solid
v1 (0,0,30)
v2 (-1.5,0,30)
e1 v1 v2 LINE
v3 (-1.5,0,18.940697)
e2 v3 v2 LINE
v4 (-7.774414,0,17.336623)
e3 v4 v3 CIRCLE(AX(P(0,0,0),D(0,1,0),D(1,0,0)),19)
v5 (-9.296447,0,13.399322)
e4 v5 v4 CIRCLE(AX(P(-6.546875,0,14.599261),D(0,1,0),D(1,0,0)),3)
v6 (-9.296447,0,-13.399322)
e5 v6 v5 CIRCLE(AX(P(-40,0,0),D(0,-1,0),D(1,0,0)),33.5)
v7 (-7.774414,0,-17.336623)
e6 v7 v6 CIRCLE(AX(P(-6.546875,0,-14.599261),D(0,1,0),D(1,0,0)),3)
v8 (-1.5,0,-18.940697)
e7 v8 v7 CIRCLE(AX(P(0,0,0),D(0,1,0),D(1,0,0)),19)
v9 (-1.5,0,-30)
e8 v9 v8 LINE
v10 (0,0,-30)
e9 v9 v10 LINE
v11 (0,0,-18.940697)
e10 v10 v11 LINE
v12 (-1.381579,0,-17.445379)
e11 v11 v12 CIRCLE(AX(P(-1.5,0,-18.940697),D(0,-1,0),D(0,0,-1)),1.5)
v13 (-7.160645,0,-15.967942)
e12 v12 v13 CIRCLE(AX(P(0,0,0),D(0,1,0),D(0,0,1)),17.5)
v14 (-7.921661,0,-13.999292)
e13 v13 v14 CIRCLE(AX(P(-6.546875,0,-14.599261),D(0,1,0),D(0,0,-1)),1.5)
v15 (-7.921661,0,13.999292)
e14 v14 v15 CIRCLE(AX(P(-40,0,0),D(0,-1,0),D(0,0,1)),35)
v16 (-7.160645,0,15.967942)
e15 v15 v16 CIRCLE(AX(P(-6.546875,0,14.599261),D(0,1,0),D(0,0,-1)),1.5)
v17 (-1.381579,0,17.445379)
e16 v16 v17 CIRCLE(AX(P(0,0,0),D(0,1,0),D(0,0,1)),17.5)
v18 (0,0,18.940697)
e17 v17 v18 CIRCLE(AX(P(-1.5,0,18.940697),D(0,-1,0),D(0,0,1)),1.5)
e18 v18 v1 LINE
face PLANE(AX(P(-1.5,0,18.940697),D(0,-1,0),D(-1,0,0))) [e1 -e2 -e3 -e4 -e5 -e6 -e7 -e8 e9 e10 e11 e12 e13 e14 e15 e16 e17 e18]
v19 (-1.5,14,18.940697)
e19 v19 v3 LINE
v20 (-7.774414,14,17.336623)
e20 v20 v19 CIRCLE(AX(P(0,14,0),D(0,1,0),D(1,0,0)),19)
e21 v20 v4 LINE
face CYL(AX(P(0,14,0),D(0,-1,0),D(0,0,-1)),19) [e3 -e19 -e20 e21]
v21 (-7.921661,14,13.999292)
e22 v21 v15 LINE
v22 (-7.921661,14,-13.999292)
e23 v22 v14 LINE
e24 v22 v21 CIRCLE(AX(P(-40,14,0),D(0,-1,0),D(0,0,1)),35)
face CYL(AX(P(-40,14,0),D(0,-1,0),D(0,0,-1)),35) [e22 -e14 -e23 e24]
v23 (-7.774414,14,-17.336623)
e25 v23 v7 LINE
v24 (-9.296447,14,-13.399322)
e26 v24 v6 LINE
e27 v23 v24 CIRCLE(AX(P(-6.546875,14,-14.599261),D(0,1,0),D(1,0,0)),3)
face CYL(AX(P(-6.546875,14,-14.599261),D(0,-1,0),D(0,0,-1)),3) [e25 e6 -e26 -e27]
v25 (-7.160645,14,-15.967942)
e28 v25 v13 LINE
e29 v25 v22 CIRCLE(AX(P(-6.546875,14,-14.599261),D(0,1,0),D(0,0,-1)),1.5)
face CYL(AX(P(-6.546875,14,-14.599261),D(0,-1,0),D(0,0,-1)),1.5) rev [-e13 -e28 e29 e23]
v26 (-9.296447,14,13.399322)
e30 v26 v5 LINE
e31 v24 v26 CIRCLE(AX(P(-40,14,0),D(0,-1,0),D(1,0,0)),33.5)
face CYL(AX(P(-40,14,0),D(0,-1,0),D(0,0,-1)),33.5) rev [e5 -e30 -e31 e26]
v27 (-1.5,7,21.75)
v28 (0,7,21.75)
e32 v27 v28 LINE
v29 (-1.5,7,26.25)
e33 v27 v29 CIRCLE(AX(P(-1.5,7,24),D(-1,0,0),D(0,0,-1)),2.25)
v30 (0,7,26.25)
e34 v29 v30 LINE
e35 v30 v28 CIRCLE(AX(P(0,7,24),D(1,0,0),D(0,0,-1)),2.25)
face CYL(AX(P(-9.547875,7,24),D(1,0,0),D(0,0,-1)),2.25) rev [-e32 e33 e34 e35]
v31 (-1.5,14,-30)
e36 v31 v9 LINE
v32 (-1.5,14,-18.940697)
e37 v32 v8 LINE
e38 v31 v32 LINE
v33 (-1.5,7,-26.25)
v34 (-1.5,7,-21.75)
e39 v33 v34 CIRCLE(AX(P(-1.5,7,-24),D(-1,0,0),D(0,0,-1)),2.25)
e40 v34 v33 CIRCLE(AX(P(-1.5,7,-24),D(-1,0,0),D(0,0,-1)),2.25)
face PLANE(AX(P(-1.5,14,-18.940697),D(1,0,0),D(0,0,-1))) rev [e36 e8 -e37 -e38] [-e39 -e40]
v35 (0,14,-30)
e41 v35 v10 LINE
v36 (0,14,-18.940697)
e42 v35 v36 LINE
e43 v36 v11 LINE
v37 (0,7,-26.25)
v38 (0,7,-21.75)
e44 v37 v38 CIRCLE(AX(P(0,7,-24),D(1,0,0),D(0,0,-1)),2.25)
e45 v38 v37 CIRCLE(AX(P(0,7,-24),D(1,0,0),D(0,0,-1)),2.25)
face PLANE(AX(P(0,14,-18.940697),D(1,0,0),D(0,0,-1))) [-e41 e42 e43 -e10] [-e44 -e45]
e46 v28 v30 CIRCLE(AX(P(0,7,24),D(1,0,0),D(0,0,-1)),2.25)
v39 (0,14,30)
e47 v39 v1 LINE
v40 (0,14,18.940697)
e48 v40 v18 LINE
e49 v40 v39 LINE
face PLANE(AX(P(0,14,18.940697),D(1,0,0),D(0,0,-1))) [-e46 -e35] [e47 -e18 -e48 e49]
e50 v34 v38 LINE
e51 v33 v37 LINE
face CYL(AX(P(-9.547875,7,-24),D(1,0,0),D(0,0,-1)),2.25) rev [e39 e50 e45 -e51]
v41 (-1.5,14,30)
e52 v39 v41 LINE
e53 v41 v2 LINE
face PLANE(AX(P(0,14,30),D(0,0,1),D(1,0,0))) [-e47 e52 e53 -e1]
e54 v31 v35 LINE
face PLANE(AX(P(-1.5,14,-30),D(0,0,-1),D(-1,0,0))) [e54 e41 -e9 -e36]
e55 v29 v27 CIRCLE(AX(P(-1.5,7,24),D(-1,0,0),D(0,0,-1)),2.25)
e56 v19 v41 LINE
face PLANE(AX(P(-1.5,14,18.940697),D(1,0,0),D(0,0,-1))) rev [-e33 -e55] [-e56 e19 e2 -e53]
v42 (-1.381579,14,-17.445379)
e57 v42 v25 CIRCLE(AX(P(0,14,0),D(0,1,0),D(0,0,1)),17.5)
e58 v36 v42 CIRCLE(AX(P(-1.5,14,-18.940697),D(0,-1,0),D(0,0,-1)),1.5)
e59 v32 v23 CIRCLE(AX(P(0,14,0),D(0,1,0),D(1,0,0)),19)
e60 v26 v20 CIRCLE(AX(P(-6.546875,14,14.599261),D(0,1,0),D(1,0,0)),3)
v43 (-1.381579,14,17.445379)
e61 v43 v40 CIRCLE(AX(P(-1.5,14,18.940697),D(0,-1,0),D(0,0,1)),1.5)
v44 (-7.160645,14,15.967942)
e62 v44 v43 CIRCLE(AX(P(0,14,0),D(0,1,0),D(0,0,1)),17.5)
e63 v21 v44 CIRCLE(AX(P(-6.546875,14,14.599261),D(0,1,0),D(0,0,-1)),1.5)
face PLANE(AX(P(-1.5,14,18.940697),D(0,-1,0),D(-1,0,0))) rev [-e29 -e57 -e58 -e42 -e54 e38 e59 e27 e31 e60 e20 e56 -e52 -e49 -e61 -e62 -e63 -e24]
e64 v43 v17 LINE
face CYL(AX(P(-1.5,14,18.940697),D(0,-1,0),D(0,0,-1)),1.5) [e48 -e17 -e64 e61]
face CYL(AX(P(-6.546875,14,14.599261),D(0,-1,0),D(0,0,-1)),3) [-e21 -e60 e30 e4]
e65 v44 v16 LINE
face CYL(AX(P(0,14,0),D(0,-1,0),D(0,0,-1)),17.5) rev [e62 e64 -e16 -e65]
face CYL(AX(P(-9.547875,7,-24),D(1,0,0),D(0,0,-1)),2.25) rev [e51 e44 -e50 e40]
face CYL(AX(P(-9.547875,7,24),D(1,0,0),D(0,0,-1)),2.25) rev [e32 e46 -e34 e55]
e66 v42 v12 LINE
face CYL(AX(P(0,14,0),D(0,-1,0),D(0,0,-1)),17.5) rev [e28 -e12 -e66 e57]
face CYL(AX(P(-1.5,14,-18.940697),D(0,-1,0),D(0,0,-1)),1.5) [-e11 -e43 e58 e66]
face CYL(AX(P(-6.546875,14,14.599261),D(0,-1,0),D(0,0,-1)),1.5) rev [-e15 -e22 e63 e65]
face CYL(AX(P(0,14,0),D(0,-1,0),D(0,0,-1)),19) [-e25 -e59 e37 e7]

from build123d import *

# Parameters (mm, degrees)
EXTRUDE_THIN3_DEPTH = 14
CUT_EXTRUDE2_REACH  = 36.455
SKETCH3_R           = 2.25


with BuildPart() as part:
    # Sketch1 → Extrude-Thin3 (new body)
    with BuildSketch(Plane(origin=(0, 0, 0), x_dir=(1, 0, 0), z_dir=(0, 1, 0))):
        with BuildLine():
            Line((0, -30), (0, -18.940696925))
            ThreePointArc((0, -18.940696925), (-0.398266916, -17.922765586), (-1.381578947, -17.445378747))
            ThreePointArc((-1.381578947, -17.445378747), (-4.334524238, -16.954701402), (-7.160644531, -15.967941943))
            ThreePointArc((-7.160644531, -15.967941943), (-7.945976251, -15.140108401), (-7.921660959, -13.999291567))
            ThreePointArc((-7.921660959, -13.999291567), (-5, 0), (-7.921660959, 13.999291567))
            ThreePointArc((-7.921660959, 13.999291567), (-7.945976251, 15.140108401), (-7.160644531, 15.967941943))
            ThreePointArc((-7.160644531, 15.967941943), (-4.334524238, 16.954701402), (-1.381578947, 17.445378747))
            ThreePointArc((-1.381578947, 17.445378747), (-0.398266916, 17.922765586), (0, 18.940696925))
            Line((0, 18.940696925), (0, 30))
            Line((0, 30), (-1.5, 30))
            Line((-1.5, 30), (-1.5, 18.940696925))
            ThreePointArc((-1.5, 18.940696925), (-4.706054887, 18.407961522), (-7.774414062, 17.336622681))
            ThreePointArc((-7.774414063, 17.336622681), (-9.345077502, 15.680955597), (-9.296446918, 13.399321928))
            ThreePointArc((-9.296446918, 13.399321928), (-6.5, 0), (-9.296446918, -13.399321928))
            ThreePointArc((-9.296446918, -13.399321928), (-9.345077502, -15.680955597), (-7.774414062, -17.336622681))
            ThreePointArc((-7.774414063, -17.336622681), (-4.706054887, -18.407961522), (-1.5, -18.940696925))
            Line((-1.5, -18.940696925), (-1.5, -30))
            Line((-1.5, -30), (0, -30))
        make_face()
    extrude(amount=EXTRUDE_THIN3_DEPTH)

    # Sketch3 → Cut-Extrude2 (cut, up to next)
    with BuildSketch(Plane(origin=(0, 0, 0), x_dir=(0, 0, -1), z_dir=(1, 0, 0)), mode=Mode.PRIVATE) as cut_extrude2_sk1:
        with Locations((-24, 7)):
            Circle(SKETCH3_R)
    cut_extrude2_tool1 = extrude(cut_extrude2_sk1.sketch, amount=-CUT_EXTRUDE2_REACH, mode=Mode.PRIVATE) & part.part
    # Sketch3 → Cut-Extrude2 (cut, up to next)
    with BuildSketch(Plane(origin=(0, 0, 0), x_dir=(0, 0, -1), z_dir=(1, 0, 0)), mode=Mode.PRIVATE) as cut_extrude2_sk2:
        with Locations((24, 7)):
            Circle(SKETCH3_R)
    cut_extrude2_tool2 = extrude(cut_extrude2_sk2.sketch, amount=-CUT_EXTRUDE2_REACH, mode=Mode.PRIVATE) & part.part
    add(cut_extrude2_tool1.solids().sort_by_distance((0, 7, 24))[0], mode=Mode.SUBTRACT)
    add(cut_extrude2_tool2.solids().sort_by_distance((0, 7, -24))[0], mode=Mode.SUBTRACT)


solid = part.part
